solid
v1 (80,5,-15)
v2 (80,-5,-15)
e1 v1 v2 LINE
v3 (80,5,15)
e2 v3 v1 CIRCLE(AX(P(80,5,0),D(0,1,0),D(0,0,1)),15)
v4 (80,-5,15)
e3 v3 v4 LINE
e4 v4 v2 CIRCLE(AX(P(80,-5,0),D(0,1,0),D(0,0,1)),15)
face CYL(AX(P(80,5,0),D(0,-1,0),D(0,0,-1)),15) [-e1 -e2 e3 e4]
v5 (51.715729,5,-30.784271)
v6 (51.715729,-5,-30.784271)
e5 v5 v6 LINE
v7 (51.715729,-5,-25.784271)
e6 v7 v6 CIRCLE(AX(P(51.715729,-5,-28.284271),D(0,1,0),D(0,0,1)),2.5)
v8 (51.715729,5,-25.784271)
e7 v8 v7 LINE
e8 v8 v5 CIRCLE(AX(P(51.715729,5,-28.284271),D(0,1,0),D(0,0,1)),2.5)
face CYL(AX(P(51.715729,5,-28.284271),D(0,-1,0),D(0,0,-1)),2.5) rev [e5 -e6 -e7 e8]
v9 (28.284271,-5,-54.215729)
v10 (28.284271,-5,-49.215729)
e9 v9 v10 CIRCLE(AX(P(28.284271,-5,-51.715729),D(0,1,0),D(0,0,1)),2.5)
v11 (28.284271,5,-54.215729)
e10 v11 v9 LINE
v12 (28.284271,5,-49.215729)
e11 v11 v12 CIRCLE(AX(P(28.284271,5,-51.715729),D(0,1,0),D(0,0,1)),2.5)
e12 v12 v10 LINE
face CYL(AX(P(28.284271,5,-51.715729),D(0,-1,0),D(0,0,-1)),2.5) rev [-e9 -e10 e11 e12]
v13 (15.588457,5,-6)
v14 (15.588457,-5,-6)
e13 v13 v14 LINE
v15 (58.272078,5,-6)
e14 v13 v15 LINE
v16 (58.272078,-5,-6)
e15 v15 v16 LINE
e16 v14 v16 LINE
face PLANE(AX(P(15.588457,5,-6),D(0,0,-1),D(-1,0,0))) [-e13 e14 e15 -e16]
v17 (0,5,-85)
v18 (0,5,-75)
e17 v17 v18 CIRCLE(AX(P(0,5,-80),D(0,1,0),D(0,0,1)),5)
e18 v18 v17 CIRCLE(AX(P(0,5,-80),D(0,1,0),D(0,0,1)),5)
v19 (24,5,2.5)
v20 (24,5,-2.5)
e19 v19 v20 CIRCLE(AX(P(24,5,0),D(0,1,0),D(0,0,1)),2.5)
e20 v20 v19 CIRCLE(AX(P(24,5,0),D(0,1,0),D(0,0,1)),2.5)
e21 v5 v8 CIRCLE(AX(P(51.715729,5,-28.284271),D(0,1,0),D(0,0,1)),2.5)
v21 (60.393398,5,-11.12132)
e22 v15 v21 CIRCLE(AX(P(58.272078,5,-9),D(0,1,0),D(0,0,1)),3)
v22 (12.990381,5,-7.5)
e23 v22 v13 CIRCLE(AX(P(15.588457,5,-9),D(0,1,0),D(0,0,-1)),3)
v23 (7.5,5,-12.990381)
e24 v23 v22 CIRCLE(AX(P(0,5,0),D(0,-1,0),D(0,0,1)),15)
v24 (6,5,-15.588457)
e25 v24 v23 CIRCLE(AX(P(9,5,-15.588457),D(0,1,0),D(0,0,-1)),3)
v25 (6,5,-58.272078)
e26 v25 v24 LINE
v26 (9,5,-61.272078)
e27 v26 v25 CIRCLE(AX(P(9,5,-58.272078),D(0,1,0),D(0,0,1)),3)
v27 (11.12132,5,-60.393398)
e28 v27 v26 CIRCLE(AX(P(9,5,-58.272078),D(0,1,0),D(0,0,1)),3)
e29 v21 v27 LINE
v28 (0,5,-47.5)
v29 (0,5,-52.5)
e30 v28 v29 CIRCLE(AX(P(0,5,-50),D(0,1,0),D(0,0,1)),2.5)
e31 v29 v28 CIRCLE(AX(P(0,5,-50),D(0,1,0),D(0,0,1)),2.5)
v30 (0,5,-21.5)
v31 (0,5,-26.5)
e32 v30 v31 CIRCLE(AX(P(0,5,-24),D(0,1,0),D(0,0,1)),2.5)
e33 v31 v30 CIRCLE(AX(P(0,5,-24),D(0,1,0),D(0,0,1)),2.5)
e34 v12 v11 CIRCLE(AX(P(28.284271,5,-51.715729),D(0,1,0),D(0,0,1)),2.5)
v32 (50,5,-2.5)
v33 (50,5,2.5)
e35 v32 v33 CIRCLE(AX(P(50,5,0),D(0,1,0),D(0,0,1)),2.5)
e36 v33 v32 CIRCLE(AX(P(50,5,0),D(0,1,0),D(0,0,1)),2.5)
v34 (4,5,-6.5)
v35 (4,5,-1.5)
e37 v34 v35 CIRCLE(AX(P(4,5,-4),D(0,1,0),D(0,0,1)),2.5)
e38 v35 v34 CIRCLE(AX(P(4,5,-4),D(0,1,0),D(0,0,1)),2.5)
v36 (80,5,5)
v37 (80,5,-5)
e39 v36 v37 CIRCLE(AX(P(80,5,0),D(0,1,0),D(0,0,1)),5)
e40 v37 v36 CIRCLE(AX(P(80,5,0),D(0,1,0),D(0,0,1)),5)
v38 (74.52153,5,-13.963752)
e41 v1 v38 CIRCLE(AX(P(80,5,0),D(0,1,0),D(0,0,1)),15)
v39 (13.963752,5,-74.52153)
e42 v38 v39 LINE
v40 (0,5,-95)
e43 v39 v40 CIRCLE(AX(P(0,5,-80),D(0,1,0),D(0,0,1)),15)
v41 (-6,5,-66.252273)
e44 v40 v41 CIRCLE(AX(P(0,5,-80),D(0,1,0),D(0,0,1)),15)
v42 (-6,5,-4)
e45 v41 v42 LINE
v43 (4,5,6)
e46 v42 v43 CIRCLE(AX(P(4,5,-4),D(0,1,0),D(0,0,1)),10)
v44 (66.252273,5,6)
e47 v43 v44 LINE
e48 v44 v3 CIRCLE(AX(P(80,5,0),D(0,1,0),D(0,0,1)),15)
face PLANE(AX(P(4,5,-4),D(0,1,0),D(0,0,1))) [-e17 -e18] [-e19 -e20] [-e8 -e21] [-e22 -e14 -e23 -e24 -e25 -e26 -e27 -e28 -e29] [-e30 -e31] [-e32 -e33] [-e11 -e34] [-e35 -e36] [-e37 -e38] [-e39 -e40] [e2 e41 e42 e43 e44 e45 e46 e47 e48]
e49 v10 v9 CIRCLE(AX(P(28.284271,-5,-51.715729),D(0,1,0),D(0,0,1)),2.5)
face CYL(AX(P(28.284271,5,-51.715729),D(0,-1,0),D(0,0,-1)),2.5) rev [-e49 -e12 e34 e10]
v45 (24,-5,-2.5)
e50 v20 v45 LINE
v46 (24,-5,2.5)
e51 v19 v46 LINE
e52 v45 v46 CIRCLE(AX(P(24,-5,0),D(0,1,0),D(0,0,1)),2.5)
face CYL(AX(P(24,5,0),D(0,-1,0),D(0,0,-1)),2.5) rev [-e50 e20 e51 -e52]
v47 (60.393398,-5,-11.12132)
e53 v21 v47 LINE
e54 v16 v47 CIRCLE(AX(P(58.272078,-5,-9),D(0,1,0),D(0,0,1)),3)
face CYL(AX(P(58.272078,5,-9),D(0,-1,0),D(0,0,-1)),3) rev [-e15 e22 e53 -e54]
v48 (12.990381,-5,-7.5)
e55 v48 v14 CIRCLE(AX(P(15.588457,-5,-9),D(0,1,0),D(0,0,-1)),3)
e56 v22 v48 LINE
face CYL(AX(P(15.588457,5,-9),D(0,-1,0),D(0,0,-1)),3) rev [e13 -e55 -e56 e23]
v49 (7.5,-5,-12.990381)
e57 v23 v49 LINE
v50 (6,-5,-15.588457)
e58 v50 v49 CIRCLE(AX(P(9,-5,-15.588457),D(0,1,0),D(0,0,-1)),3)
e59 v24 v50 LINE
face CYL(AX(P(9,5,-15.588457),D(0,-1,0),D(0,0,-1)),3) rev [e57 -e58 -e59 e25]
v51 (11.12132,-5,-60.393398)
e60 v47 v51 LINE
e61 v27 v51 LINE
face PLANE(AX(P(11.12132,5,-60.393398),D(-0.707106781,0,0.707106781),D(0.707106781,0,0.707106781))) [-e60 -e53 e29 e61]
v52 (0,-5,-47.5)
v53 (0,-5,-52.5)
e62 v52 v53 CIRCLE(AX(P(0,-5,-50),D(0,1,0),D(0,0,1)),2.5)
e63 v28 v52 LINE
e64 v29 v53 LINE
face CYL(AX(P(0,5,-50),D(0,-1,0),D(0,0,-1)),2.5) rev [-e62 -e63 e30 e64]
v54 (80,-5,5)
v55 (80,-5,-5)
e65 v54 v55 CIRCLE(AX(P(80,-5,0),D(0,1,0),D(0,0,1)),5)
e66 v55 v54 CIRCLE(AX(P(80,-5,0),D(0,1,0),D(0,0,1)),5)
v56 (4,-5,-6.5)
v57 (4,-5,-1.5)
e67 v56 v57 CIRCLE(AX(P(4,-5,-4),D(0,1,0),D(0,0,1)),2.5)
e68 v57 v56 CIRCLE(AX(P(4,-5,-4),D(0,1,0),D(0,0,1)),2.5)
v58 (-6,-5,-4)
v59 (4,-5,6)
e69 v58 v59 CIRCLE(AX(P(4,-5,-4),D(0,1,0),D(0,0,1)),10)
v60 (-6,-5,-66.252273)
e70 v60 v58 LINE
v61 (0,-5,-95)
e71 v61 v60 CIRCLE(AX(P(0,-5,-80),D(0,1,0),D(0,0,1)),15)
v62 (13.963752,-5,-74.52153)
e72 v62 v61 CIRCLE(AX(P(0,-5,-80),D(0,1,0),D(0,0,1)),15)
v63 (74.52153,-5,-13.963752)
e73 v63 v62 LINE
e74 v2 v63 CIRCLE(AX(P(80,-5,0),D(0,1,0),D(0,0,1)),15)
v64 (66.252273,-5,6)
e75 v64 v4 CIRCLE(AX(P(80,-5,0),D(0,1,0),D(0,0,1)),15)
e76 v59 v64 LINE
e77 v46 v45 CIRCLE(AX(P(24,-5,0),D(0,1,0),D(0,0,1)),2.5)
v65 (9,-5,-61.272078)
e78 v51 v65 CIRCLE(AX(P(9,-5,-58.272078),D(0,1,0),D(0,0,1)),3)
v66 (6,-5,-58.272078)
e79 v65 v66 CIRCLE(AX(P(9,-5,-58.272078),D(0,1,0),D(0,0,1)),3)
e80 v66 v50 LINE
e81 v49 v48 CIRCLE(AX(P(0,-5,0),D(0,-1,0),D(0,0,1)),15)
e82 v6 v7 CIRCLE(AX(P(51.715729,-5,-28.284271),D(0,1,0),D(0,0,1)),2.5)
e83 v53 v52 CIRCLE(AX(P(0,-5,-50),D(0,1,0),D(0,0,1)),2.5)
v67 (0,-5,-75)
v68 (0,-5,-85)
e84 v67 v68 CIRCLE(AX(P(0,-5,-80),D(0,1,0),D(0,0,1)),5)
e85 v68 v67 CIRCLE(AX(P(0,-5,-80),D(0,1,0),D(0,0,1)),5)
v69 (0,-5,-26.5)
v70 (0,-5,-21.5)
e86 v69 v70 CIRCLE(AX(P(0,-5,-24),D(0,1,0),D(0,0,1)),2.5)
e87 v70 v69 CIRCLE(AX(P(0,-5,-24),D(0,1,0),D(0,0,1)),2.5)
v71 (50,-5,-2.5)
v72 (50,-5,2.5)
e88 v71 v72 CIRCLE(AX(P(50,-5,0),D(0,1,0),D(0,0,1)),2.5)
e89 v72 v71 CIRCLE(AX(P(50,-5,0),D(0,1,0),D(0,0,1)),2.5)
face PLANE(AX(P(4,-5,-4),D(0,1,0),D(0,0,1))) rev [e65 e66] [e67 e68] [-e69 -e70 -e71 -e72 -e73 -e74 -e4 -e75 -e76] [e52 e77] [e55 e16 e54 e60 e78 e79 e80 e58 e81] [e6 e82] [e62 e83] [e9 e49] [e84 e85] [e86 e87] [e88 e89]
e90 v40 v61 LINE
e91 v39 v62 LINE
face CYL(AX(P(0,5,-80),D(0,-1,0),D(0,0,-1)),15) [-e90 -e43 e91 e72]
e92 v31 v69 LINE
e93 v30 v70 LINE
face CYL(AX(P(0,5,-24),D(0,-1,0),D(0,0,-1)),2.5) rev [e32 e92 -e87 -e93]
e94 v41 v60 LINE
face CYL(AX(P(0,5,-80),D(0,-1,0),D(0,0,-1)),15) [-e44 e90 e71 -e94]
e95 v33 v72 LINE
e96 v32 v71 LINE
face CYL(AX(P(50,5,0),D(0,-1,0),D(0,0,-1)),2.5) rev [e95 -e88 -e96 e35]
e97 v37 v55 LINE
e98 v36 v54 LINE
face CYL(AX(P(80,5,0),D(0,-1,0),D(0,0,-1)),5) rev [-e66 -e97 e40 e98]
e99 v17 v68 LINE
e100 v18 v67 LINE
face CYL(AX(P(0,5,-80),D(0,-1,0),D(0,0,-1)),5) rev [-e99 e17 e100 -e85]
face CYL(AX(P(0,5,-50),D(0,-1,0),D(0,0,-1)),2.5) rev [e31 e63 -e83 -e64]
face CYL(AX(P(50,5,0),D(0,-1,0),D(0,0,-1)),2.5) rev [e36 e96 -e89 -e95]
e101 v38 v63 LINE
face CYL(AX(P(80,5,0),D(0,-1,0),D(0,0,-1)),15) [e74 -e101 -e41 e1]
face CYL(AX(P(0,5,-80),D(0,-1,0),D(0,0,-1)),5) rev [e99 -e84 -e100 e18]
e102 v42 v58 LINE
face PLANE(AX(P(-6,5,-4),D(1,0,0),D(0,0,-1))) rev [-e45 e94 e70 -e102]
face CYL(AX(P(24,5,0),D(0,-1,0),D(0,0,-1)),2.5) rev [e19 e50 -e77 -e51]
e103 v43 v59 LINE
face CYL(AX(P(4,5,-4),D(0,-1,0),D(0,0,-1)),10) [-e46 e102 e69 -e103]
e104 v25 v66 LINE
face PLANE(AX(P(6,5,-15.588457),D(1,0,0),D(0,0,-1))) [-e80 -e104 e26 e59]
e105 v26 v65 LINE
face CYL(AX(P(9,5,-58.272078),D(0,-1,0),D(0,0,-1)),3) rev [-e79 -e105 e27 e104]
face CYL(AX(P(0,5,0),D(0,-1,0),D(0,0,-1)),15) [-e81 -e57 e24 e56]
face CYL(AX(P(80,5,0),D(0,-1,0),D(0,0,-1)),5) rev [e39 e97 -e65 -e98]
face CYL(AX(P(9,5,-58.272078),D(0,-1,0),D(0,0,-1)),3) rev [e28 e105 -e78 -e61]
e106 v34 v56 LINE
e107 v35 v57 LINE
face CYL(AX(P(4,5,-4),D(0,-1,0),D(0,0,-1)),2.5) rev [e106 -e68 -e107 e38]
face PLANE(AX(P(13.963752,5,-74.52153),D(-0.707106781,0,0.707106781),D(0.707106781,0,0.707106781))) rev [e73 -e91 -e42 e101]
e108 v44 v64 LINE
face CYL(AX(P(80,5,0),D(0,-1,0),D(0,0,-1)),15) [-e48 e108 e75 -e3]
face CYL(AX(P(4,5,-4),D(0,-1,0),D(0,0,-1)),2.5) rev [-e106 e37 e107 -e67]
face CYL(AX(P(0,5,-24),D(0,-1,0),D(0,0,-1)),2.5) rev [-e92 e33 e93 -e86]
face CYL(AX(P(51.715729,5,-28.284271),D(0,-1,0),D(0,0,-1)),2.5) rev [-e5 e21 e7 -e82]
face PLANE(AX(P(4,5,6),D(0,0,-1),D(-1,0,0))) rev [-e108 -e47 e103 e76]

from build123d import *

# Parameters (mm, degrees)
WEB_PLATE_PROFILE_R          = 5
WEB_PLATE_PROFILE_R_2        = 2.5
WEB_PLATE_EXTRUDE_10MM_DEPTH = 5


with BuildPart() as part:
    # Web Plate Profile → Web Plate Extrude 10mm (new, symmetric)
    with BuildSketch(Plane(origin=(0, 0, 0), x_dir=(1, 0, 0), z_dir=(0, 1, 0))):
        with BuildLine():
            Line((-6, 4), (-6, 66.252272915))
            ThreePointArc((-6, 66.252272915), (-5.740251485, 93.858192988), (13.963751735, 74.52152964))
            Line((13.963751735, 74.52152964), (74.52152964, 13.963751735))
            ThreePointArc((74.52152964, 13.963751735), (93.858192988, -5.740251485), (66.252272915, -6))
            Line((66.252272915, -6), (4, -6))
            ThreePointArc((4, -6), (-3.071067812, -3.071067812), (-6, 4))
        make_face()
        with Locations(Location((0, 80, 0), (0, 0, 270))):
            Circle(WEB_PLATE_PROFILE_R, mode=Mode.SUBTRACT)
        with Locations(Location((80, 0, 0), (0, 0, 270))):
            Circle(WEB_PLATE_PROFILE_R, mode=Mode.SUBTRACT)
        with Locations(Location((4, 4, 0), (0, 0, 270))):
            Circle(WEB_PLATE_PROFILE_R_2, mode=Mode.SUBTRACT)
        with Locations(Location((50, 0, 0), (0, 0, 270))):
            Circle(WEB_PLATE_PROFILE_R_2, mode=Mode.SUBTRACT)
        with Locations(Location((24, 0, 0), (0, 0, 270))):
            Circle(WEB_PLATE_PROFILE_R_2, mode=Mode.SUBTRACT)
        with Locations(Location((0, 24, 0), (0, 0, 270))):
            Circle(WEB_PLATE_PROFILE_R_2, mode=Mode.SUBTRACT)
        with Locations(Location((0, 50, 0), (0, 0, 270))):
            Circle(WEB_PLATE_PROFILE_R_2, mode=Mode.SUBTRACT)
        with Locations(Location((28.284271247, 51.715728753, 0), (0, 0, 270))):
            Circle(WEB_PLATE_PROFILE_R_2, mode=Mode.SUBTRACT)
        with Locations(Location((51.715728753, 28.284271247, 0), (0, 0, 270))):
            Circle(WEB_PLATE_PROFILE_R_2, mode=Mode.SUBTRACT)
        with BuildLine():
            Line((11.121320344, 60.393398282), (60.393398282, 11.121320344))
            ThreePointArc((60.393398282, 11.121320344), (61.043716536, 7.851949703), (58.272077939, 6))
            Line((58.272077939, 6), (15.588457268, 6))
            ThreePointArc((15.588457268, 6), (14.088457268, 6.401923789), (12.990381057, 7.5))
            ThreePointArc((12.990381057, 7.5), (10.606601718, 10.606601718), (7.5, 12.990381057))
            ThreePointArc((7.5, 12.990381057), (6.401923789, 14.088457268), (6, 15.588457268))
            Line((6, 15.588457268), (6, 58.272077939))
            ThreePointArc((6, 58.272077939), (7.851949703, 61.043716536), (11.121320344, 60.393398282))
        make_face(mode=Mode.SUBTRACT)
    extrude(amount=WEB_PLATE_EXTRUDE_10MM_DEPTH, both=True)


solid = part.part
